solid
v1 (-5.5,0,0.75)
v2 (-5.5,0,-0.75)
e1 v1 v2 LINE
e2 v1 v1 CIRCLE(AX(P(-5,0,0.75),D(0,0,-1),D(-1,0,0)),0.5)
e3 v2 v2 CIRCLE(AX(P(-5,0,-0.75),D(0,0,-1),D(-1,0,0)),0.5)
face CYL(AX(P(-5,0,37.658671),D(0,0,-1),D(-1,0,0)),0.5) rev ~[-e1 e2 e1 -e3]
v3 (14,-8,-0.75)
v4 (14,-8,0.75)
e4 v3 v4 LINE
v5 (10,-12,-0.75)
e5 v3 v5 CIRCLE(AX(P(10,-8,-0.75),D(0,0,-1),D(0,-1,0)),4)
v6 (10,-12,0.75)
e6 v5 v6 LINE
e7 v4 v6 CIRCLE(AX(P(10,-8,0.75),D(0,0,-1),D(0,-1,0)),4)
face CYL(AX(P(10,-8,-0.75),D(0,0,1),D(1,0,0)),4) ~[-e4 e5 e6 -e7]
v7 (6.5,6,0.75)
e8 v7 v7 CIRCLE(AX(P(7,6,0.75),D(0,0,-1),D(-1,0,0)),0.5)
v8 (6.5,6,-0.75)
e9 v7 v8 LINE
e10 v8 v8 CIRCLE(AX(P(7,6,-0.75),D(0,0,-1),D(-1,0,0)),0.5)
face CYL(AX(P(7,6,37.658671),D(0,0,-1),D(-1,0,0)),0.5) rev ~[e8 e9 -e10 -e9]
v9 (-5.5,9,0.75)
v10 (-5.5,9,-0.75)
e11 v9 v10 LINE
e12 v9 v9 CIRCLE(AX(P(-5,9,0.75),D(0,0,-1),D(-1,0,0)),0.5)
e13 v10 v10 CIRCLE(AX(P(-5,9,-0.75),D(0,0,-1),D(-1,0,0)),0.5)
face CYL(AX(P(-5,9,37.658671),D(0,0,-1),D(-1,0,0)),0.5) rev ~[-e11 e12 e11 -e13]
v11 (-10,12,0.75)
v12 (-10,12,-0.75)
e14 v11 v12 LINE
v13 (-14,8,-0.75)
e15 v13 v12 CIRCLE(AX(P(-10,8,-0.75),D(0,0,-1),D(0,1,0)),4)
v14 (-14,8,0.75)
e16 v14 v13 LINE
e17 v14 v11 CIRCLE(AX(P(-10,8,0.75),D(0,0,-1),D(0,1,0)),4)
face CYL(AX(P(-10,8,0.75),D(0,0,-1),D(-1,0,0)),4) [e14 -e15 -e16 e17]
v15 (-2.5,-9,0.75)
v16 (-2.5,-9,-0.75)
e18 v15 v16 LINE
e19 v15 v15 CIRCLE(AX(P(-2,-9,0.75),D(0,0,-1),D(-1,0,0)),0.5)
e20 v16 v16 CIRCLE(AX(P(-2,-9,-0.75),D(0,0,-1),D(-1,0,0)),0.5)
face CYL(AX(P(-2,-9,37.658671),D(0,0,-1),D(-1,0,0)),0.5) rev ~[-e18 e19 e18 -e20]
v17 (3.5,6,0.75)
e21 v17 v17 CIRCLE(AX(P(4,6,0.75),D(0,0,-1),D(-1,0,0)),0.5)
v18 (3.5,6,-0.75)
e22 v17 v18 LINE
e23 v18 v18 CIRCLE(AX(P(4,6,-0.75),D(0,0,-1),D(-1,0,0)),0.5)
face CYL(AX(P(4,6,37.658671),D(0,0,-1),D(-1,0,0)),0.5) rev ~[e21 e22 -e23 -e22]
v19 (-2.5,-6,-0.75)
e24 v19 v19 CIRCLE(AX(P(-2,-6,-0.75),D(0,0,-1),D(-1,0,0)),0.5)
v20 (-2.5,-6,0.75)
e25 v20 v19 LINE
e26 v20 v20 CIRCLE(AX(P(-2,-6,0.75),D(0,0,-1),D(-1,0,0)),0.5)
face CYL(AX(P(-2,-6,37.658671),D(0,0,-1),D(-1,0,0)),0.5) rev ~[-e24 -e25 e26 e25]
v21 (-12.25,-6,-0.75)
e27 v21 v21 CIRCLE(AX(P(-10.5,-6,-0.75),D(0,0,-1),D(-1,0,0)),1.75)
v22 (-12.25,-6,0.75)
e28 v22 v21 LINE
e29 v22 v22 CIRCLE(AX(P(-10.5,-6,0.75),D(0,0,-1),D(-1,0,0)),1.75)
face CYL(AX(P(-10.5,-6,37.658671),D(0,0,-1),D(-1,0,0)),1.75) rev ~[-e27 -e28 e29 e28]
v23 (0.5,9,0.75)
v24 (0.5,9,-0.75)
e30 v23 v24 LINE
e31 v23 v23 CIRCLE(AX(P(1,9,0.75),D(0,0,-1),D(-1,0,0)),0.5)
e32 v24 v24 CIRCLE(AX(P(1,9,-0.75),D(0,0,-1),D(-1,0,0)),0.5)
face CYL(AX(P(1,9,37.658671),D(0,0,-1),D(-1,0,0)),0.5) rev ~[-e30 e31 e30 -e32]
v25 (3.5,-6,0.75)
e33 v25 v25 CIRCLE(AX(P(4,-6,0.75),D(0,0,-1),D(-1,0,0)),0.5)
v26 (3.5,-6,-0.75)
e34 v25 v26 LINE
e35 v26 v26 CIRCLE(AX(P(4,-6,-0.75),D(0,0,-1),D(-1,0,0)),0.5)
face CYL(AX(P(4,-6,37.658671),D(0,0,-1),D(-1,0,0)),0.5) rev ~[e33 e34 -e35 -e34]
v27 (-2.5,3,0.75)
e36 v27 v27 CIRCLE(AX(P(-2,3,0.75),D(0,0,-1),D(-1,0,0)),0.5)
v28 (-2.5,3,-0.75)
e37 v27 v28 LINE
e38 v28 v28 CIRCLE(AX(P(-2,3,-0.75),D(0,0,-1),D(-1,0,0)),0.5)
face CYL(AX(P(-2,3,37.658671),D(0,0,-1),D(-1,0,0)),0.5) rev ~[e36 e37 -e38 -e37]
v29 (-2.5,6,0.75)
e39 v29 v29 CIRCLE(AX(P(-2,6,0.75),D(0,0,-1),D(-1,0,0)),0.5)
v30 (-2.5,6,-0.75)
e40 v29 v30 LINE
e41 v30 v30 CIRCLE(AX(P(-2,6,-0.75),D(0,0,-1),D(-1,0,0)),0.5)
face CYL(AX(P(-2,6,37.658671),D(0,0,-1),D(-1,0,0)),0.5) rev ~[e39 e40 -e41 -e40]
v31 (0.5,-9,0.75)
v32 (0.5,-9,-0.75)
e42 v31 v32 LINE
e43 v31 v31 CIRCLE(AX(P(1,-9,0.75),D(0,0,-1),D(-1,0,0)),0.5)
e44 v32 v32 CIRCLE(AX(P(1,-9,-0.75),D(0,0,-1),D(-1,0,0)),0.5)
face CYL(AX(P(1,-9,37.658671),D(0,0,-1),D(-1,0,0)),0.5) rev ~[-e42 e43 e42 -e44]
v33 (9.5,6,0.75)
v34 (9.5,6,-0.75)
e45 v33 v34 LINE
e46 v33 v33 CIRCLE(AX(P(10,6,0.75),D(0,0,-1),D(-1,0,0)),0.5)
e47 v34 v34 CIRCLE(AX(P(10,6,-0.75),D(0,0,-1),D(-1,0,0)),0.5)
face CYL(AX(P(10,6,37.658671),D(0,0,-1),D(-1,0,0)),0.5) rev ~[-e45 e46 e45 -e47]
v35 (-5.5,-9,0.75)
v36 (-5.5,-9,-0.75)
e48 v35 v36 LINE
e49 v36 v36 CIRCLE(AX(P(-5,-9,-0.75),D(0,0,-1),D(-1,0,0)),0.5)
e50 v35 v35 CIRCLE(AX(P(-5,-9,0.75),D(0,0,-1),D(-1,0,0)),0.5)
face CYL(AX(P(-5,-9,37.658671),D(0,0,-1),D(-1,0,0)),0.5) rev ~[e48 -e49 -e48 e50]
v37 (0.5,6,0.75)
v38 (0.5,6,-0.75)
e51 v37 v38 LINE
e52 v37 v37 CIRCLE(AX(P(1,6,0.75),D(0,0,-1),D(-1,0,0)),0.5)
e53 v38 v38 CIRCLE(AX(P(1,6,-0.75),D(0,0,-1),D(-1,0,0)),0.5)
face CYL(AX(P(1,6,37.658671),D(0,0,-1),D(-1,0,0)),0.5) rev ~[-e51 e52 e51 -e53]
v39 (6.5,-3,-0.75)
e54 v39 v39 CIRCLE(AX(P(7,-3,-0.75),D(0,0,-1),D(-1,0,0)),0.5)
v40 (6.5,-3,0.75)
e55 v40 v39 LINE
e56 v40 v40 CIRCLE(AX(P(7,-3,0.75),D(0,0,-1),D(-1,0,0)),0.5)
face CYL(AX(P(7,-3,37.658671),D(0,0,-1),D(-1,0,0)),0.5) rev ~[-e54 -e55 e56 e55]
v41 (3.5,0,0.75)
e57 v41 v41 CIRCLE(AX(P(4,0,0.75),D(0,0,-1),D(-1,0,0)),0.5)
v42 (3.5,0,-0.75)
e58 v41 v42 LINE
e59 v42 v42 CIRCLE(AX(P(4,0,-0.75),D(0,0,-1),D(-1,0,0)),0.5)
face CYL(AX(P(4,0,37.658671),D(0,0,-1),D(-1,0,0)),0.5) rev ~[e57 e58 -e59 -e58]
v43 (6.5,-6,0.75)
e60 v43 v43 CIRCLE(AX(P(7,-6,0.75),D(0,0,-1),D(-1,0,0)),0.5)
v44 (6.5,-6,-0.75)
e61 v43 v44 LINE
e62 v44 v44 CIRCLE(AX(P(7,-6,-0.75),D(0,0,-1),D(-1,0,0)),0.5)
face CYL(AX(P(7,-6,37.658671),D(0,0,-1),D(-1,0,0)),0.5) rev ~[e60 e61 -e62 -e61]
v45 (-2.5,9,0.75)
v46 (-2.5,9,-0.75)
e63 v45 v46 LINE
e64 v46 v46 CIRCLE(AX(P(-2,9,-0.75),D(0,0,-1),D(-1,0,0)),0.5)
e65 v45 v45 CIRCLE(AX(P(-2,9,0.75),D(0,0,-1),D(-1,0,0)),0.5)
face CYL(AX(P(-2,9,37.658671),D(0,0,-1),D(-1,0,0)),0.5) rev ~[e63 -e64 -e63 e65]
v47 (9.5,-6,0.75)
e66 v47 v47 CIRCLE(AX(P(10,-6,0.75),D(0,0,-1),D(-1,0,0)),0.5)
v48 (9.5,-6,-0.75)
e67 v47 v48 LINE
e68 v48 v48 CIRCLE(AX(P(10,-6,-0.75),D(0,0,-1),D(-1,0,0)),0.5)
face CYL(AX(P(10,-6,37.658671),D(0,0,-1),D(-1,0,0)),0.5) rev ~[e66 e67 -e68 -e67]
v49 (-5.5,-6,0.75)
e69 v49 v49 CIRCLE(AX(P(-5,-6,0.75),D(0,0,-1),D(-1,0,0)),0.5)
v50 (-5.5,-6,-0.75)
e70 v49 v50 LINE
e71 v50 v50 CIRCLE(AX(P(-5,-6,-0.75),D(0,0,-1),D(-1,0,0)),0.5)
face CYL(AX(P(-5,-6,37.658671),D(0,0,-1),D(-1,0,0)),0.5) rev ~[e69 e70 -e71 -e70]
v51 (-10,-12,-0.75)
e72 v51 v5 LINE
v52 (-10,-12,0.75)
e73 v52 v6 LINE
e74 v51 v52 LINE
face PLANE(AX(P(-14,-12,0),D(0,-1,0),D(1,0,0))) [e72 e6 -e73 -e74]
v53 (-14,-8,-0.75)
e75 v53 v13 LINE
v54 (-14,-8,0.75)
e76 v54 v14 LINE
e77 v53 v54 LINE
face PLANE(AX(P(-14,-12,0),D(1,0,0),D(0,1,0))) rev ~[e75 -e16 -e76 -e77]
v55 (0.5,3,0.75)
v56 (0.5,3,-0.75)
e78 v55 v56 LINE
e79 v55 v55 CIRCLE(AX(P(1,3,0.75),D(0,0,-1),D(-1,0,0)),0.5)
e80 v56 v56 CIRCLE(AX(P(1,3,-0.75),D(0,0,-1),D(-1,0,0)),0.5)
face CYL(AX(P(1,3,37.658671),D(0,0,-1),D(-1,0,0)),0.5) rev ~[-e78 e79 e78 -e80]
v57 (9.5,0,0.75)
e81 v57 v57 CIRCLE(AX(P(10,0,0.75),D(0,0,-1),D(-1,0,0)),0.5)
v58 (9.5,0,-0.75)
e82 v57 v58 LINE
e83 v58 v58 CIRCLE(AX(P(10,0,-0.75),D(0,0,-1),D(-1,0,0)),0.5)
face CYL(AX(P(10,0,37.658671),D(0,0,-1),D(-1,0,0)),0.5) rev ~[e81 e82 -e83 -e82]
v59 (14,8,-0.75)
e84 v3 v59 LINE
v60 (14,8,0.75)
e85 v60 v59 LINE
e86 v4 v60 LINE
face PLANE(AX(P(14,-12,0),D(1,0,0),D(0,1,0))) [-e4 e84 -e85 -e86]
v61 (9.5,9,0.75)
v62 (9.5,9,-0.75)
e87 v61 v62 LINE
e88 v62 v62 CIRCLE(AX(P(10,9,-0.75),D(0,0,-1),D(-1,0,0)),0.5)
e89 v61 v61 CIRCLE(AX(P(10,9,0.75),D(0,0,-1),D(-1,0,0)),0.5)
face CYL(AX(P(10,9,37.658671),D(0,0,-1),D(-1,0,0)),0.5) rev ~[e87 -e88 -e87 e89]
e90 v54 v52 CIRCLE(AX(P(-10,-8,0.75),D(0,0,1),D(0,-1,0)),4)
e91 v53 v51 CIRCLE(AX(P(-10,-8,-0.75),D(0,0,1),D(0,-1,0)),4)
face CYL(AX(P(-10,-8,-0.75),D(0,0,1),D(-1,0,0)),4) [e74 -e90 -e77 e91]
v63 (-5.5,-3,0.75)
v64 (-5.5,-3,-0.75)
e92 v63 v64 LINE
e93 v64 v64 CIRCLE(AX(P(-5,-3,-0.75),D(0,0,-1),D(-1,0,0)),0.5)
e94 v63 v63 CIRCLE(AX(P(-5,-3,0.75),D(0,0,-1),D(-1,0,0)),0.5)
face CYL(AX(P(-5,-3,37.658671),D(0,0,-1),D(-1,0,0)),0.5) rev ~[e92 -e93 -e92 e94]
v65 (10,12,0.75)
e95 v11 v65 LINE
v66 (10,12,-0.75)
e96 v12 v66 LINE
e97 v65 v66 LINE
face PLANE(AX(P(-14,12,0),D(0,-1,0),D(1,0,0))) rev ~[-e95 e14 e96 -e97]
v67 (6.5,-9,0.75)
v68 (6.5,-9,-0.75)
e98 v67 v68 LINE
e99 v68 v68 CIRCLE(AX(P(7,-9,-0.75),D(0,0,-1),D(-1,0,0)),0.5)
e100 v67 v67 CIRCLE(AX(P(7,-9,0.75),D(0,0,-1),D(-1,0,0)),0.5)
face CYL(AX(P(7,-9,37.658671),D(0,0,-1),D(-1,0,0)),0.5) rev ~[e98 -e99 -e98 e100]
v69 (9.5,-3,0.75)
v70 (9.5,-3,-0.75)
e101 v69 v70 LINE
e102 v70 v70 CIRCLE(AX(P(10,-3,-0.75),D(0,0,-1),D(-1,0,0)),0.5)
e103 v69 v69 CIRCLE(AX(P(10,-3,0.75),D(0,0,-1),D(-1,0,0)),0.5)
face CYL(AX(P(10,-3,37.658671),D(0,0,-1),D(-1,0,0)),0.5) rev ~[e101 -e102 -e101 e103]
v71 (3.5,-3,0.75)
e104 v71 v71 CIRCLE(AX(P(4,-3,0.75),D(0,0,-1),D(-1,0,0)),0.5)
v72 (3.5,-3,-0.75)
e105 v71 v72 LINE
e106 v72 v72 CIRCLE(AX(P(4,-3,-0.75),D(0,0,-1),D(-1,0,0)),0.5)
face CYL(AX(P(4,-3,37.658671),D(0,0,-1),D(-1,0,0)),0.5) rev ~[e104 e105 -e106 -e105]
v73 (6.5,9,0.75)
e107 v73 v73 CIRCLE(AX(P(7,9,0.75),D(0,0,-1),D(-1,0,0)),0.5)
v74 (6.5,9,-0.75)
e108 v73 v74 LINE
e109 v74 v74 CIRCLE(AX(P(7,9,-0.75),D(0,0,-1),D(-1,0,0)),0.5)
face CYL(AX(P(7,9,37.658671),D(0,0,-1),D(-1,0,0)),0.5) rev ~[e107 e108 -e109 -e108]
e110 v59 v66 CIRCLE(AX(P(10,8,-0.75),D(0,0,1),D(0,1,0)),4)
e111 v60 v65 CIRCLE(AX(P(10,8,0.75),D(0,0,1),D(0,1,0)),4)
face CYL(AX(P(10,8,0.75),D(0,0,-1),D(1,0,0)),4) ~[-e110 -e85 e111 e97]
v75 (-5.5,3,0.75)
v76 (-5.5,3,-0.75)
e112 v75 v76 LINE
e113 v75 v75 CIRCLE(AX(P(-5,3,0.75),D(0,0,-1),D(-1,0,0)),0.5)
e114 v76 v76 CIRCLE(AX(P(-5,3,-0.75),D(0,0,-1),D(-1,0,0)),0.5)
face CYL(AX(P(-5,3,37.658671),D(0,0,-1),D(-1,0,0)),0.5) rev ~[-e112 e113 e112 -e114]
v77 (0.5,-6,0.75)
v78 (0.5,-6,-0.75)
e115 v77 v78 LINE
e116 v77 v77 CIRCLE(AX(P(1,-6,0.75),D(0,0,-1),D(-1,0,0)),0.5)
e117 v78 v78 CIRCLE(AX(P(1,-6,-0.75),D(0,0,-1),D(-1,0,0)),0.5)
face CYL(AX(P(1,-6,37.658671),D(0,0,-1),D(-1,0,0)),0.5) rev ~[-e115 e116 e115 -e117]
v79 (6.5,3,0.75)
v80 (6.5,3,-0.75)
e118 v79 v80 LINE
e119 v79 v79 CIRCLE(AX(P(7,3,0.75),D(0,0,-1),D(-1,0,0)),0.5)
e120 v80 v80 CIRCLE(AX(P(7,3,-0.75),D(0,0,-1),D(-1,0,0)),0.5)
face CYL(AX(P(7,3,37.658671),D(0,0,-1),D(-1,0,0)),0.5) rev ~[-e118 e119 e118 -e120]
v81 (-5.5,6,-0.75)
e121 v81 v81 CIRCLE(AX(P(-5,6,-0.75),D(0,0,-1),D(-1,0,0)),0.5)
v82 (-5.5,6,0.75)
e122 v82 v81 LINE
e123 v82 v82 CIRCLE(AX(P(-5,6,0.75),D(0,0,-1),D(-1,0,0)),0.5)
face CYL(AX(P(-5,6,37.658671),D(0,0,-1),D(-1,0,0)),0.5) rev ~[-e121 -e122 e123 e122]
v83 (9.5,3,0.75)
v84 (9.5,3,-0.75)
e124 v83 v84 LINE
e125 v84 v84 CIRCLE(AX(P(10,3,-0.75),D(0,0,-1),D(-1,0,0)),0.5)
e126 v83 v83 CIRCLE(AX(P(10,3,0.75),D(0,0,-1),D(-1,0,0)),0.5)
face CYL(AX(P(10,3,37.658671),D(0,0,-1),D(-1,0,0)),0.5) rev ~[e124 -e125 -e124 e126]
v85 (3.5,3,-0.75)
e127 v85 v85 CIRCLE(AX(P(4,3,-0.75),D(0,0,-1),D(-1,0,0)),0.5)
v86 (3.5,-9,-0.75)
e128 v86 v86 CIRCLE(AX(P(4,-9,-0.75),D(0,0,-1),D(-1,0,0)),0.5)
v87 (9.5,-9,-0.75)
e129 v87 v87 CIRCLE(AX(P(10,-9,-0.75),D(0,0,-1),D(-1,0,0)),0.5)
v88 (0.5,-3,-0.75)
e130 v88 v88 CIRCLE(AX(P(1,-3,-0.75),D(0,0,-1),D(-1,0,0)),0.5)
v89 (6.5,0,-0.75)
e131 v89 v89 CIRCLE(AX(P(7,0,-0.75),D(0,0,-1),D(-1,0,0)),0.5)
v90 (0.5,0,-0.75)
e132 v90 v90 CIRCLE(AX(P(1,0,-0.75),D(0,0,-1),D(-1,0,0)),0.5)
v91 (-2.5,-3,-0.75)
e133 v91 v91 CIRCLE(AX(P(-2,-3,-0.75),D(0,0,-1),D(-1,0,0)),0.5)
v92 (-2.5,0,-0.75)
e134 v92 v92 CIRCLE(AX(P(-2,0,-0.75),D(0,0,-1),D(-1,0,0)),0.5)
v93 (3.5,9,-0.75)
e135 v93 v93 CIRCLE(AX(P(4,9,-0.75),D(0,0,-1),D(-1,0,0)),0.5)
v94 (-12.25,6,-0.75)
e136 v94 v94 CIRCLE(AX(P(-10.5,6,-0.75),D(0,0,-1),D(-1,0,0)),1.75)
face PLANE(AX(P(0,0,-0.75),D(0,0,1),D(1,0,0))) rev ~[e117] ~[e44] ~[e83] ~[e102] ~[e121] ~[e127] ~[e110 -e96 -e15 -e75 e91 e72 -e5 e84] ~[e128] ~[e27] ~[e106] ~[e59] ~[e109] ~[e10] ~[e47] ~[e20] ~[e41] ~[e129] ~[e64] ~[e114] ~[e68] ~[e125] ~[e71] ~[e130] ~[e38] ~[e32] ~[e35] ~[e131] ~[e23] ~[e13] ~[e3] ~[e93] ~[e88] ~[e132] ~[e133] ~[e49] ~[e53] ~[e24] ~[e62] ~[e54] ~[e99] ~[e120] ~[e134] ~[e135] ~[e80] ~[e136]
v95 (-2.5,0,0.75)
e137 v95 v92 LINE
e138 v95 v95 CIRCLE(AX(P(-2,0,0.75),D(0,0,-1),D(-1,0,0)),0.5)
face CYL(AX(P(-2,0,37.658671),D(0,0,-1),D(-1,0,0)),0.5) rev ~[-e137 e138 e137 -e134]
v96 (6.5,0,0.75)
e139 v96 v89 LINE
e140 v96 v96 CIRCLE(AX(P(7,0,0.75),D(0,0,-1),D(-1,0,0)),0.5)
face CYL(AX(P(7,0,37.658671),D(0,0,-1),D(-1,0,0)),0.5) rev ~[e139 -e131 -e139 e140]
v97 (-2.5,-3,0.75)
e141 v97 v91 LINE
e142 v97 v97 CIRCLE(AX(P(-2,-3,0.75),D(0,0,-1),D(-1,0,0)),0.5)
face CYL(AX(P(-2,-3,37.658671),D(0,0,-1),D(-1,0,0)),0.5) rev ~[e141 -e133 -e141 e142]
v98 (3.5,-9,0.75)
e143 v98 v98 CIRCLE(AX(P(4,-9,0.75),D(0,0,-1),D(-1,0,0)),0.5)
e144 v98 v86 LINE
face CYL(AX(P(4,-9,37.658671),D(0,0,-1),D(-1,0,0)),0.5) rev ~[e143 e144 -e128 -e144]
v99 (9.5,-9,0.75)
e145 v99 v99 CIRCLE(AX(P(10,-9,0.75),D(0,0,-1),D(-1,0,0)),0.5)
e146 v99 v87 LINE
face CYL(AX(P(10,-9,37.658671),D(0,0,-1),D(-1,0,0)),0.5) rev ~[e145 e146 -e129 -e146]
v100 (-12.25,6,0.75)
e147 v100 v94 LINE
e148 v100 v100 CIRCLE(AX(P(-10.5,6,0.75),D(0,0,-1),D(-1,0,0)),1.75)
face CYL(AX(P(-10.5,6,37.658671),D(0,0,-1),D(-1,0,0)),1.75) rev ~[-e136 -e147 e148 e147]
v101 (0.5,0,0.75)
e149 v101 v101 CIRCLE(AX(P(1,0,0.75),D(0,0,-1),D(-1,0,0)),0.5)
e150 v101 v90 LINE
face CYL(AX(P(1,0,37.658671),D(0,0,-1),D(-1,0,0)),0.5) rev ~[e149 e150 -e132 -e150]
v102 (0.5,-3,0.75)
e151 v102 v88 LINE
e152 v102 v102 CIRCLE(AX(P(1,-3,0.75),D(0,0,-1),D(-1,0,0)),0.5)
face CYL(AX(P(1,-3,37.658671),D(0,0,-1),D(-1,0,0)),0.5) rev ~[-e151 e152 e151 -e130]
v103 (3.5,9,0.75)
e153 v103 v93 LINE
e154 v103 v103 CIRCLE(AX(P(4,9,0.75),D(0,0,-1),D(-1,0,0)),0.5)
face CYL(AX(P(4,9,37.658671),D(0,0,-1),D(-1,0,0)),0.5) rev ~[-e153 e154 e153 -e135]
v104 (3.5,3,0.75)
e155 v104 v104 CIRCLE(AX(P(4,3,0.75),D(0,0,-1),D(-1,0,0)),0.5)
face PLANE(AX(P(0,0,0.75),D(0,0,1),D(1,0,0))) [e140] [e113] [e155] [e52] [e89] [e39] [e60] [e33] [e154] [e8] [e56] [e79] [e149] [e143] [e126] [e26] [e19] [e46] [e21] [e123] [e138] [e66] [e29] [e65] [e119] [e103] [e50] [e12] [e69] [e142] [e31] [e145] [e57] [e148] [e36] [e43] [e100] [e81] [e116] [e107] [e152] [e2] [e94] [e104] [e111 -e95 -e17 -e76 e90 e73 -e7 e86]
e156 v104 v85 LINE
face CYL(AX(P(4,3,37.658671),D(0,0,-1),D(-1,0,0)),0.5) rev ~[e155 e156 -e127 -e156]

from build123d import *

# Parameters (mm, degrees)
SKETCH1_W                  = 28
SKETCH1_H                  = 24
BOSS_EXTRUDE1_DEPTH        = 0.75
FILLET1_R                  = 4
F_3_5_3_5_DIAMETER_HOLE1_D = 3.5
F_1_0_1_DIAMETER_HOLE1_D   = 1
LPATTERN1_COUNT            = 6
LPATTERN1_PITCH            = 3
LPATTERN1_COUNT_DIR2       = 7
LPATTERN1_PITCH_DIR2       = 3


with BuildPart() as part:
    # Sketch1 → Boss-Extrude1 (new, symmetric)
    with BuildSketch(Plane.XY):
        Rectangle(SKETCH1_W, SKETCH1_H)
    extrude(amount=BOSS_EXTRUDE1_DEPTH, both=True)

    # Fillet1
    fillet1_edges = [part.edges().sort_by_distance(p)[0] for p in [
        (14, -12, 0),
        (-14, -12, 0),
        (-14, 12, 0),
        (14, 12, 0),
    ]]
    fillet(fillet1_edges, radius=FILLET1_R)

    # Ø3.5 (3.5) Diameter Hole1 (through all)
    with Locations(Plane.XY.offset(0.75)):
        with Locations((-10.5, 6), (-10.5, -6)):
            Hole(F_3_5_3_5_DIAMETER_HOLE1_D / 2)

    # Ø1.0 (1) Diameter Hole1 (through all)
    with Locations(Plane.XY.offset(0.75)):
        with Locations((10, -9)):
            f_1_0_1_diameter_hole1 = Hole(F_1_0_1_DIAMETER_HOLE1_D / 2)

    # LPattern1: 1.0 _1_ Diameter Hole1 6 × 7
    with Locations(*[(-i * LPATTERN1_PITCH, j * LPATTERN1_PITCH_DIR2, 0) for i in range(LPATTERN1_COUNT) for j in range(LPATTERN1_COUNT_DIR2) if (i, j) != (0, 0)]):
        add(f_1_0_1_diameter_hole1, mode=Mode.SUBTRACT)


solid = part.part
